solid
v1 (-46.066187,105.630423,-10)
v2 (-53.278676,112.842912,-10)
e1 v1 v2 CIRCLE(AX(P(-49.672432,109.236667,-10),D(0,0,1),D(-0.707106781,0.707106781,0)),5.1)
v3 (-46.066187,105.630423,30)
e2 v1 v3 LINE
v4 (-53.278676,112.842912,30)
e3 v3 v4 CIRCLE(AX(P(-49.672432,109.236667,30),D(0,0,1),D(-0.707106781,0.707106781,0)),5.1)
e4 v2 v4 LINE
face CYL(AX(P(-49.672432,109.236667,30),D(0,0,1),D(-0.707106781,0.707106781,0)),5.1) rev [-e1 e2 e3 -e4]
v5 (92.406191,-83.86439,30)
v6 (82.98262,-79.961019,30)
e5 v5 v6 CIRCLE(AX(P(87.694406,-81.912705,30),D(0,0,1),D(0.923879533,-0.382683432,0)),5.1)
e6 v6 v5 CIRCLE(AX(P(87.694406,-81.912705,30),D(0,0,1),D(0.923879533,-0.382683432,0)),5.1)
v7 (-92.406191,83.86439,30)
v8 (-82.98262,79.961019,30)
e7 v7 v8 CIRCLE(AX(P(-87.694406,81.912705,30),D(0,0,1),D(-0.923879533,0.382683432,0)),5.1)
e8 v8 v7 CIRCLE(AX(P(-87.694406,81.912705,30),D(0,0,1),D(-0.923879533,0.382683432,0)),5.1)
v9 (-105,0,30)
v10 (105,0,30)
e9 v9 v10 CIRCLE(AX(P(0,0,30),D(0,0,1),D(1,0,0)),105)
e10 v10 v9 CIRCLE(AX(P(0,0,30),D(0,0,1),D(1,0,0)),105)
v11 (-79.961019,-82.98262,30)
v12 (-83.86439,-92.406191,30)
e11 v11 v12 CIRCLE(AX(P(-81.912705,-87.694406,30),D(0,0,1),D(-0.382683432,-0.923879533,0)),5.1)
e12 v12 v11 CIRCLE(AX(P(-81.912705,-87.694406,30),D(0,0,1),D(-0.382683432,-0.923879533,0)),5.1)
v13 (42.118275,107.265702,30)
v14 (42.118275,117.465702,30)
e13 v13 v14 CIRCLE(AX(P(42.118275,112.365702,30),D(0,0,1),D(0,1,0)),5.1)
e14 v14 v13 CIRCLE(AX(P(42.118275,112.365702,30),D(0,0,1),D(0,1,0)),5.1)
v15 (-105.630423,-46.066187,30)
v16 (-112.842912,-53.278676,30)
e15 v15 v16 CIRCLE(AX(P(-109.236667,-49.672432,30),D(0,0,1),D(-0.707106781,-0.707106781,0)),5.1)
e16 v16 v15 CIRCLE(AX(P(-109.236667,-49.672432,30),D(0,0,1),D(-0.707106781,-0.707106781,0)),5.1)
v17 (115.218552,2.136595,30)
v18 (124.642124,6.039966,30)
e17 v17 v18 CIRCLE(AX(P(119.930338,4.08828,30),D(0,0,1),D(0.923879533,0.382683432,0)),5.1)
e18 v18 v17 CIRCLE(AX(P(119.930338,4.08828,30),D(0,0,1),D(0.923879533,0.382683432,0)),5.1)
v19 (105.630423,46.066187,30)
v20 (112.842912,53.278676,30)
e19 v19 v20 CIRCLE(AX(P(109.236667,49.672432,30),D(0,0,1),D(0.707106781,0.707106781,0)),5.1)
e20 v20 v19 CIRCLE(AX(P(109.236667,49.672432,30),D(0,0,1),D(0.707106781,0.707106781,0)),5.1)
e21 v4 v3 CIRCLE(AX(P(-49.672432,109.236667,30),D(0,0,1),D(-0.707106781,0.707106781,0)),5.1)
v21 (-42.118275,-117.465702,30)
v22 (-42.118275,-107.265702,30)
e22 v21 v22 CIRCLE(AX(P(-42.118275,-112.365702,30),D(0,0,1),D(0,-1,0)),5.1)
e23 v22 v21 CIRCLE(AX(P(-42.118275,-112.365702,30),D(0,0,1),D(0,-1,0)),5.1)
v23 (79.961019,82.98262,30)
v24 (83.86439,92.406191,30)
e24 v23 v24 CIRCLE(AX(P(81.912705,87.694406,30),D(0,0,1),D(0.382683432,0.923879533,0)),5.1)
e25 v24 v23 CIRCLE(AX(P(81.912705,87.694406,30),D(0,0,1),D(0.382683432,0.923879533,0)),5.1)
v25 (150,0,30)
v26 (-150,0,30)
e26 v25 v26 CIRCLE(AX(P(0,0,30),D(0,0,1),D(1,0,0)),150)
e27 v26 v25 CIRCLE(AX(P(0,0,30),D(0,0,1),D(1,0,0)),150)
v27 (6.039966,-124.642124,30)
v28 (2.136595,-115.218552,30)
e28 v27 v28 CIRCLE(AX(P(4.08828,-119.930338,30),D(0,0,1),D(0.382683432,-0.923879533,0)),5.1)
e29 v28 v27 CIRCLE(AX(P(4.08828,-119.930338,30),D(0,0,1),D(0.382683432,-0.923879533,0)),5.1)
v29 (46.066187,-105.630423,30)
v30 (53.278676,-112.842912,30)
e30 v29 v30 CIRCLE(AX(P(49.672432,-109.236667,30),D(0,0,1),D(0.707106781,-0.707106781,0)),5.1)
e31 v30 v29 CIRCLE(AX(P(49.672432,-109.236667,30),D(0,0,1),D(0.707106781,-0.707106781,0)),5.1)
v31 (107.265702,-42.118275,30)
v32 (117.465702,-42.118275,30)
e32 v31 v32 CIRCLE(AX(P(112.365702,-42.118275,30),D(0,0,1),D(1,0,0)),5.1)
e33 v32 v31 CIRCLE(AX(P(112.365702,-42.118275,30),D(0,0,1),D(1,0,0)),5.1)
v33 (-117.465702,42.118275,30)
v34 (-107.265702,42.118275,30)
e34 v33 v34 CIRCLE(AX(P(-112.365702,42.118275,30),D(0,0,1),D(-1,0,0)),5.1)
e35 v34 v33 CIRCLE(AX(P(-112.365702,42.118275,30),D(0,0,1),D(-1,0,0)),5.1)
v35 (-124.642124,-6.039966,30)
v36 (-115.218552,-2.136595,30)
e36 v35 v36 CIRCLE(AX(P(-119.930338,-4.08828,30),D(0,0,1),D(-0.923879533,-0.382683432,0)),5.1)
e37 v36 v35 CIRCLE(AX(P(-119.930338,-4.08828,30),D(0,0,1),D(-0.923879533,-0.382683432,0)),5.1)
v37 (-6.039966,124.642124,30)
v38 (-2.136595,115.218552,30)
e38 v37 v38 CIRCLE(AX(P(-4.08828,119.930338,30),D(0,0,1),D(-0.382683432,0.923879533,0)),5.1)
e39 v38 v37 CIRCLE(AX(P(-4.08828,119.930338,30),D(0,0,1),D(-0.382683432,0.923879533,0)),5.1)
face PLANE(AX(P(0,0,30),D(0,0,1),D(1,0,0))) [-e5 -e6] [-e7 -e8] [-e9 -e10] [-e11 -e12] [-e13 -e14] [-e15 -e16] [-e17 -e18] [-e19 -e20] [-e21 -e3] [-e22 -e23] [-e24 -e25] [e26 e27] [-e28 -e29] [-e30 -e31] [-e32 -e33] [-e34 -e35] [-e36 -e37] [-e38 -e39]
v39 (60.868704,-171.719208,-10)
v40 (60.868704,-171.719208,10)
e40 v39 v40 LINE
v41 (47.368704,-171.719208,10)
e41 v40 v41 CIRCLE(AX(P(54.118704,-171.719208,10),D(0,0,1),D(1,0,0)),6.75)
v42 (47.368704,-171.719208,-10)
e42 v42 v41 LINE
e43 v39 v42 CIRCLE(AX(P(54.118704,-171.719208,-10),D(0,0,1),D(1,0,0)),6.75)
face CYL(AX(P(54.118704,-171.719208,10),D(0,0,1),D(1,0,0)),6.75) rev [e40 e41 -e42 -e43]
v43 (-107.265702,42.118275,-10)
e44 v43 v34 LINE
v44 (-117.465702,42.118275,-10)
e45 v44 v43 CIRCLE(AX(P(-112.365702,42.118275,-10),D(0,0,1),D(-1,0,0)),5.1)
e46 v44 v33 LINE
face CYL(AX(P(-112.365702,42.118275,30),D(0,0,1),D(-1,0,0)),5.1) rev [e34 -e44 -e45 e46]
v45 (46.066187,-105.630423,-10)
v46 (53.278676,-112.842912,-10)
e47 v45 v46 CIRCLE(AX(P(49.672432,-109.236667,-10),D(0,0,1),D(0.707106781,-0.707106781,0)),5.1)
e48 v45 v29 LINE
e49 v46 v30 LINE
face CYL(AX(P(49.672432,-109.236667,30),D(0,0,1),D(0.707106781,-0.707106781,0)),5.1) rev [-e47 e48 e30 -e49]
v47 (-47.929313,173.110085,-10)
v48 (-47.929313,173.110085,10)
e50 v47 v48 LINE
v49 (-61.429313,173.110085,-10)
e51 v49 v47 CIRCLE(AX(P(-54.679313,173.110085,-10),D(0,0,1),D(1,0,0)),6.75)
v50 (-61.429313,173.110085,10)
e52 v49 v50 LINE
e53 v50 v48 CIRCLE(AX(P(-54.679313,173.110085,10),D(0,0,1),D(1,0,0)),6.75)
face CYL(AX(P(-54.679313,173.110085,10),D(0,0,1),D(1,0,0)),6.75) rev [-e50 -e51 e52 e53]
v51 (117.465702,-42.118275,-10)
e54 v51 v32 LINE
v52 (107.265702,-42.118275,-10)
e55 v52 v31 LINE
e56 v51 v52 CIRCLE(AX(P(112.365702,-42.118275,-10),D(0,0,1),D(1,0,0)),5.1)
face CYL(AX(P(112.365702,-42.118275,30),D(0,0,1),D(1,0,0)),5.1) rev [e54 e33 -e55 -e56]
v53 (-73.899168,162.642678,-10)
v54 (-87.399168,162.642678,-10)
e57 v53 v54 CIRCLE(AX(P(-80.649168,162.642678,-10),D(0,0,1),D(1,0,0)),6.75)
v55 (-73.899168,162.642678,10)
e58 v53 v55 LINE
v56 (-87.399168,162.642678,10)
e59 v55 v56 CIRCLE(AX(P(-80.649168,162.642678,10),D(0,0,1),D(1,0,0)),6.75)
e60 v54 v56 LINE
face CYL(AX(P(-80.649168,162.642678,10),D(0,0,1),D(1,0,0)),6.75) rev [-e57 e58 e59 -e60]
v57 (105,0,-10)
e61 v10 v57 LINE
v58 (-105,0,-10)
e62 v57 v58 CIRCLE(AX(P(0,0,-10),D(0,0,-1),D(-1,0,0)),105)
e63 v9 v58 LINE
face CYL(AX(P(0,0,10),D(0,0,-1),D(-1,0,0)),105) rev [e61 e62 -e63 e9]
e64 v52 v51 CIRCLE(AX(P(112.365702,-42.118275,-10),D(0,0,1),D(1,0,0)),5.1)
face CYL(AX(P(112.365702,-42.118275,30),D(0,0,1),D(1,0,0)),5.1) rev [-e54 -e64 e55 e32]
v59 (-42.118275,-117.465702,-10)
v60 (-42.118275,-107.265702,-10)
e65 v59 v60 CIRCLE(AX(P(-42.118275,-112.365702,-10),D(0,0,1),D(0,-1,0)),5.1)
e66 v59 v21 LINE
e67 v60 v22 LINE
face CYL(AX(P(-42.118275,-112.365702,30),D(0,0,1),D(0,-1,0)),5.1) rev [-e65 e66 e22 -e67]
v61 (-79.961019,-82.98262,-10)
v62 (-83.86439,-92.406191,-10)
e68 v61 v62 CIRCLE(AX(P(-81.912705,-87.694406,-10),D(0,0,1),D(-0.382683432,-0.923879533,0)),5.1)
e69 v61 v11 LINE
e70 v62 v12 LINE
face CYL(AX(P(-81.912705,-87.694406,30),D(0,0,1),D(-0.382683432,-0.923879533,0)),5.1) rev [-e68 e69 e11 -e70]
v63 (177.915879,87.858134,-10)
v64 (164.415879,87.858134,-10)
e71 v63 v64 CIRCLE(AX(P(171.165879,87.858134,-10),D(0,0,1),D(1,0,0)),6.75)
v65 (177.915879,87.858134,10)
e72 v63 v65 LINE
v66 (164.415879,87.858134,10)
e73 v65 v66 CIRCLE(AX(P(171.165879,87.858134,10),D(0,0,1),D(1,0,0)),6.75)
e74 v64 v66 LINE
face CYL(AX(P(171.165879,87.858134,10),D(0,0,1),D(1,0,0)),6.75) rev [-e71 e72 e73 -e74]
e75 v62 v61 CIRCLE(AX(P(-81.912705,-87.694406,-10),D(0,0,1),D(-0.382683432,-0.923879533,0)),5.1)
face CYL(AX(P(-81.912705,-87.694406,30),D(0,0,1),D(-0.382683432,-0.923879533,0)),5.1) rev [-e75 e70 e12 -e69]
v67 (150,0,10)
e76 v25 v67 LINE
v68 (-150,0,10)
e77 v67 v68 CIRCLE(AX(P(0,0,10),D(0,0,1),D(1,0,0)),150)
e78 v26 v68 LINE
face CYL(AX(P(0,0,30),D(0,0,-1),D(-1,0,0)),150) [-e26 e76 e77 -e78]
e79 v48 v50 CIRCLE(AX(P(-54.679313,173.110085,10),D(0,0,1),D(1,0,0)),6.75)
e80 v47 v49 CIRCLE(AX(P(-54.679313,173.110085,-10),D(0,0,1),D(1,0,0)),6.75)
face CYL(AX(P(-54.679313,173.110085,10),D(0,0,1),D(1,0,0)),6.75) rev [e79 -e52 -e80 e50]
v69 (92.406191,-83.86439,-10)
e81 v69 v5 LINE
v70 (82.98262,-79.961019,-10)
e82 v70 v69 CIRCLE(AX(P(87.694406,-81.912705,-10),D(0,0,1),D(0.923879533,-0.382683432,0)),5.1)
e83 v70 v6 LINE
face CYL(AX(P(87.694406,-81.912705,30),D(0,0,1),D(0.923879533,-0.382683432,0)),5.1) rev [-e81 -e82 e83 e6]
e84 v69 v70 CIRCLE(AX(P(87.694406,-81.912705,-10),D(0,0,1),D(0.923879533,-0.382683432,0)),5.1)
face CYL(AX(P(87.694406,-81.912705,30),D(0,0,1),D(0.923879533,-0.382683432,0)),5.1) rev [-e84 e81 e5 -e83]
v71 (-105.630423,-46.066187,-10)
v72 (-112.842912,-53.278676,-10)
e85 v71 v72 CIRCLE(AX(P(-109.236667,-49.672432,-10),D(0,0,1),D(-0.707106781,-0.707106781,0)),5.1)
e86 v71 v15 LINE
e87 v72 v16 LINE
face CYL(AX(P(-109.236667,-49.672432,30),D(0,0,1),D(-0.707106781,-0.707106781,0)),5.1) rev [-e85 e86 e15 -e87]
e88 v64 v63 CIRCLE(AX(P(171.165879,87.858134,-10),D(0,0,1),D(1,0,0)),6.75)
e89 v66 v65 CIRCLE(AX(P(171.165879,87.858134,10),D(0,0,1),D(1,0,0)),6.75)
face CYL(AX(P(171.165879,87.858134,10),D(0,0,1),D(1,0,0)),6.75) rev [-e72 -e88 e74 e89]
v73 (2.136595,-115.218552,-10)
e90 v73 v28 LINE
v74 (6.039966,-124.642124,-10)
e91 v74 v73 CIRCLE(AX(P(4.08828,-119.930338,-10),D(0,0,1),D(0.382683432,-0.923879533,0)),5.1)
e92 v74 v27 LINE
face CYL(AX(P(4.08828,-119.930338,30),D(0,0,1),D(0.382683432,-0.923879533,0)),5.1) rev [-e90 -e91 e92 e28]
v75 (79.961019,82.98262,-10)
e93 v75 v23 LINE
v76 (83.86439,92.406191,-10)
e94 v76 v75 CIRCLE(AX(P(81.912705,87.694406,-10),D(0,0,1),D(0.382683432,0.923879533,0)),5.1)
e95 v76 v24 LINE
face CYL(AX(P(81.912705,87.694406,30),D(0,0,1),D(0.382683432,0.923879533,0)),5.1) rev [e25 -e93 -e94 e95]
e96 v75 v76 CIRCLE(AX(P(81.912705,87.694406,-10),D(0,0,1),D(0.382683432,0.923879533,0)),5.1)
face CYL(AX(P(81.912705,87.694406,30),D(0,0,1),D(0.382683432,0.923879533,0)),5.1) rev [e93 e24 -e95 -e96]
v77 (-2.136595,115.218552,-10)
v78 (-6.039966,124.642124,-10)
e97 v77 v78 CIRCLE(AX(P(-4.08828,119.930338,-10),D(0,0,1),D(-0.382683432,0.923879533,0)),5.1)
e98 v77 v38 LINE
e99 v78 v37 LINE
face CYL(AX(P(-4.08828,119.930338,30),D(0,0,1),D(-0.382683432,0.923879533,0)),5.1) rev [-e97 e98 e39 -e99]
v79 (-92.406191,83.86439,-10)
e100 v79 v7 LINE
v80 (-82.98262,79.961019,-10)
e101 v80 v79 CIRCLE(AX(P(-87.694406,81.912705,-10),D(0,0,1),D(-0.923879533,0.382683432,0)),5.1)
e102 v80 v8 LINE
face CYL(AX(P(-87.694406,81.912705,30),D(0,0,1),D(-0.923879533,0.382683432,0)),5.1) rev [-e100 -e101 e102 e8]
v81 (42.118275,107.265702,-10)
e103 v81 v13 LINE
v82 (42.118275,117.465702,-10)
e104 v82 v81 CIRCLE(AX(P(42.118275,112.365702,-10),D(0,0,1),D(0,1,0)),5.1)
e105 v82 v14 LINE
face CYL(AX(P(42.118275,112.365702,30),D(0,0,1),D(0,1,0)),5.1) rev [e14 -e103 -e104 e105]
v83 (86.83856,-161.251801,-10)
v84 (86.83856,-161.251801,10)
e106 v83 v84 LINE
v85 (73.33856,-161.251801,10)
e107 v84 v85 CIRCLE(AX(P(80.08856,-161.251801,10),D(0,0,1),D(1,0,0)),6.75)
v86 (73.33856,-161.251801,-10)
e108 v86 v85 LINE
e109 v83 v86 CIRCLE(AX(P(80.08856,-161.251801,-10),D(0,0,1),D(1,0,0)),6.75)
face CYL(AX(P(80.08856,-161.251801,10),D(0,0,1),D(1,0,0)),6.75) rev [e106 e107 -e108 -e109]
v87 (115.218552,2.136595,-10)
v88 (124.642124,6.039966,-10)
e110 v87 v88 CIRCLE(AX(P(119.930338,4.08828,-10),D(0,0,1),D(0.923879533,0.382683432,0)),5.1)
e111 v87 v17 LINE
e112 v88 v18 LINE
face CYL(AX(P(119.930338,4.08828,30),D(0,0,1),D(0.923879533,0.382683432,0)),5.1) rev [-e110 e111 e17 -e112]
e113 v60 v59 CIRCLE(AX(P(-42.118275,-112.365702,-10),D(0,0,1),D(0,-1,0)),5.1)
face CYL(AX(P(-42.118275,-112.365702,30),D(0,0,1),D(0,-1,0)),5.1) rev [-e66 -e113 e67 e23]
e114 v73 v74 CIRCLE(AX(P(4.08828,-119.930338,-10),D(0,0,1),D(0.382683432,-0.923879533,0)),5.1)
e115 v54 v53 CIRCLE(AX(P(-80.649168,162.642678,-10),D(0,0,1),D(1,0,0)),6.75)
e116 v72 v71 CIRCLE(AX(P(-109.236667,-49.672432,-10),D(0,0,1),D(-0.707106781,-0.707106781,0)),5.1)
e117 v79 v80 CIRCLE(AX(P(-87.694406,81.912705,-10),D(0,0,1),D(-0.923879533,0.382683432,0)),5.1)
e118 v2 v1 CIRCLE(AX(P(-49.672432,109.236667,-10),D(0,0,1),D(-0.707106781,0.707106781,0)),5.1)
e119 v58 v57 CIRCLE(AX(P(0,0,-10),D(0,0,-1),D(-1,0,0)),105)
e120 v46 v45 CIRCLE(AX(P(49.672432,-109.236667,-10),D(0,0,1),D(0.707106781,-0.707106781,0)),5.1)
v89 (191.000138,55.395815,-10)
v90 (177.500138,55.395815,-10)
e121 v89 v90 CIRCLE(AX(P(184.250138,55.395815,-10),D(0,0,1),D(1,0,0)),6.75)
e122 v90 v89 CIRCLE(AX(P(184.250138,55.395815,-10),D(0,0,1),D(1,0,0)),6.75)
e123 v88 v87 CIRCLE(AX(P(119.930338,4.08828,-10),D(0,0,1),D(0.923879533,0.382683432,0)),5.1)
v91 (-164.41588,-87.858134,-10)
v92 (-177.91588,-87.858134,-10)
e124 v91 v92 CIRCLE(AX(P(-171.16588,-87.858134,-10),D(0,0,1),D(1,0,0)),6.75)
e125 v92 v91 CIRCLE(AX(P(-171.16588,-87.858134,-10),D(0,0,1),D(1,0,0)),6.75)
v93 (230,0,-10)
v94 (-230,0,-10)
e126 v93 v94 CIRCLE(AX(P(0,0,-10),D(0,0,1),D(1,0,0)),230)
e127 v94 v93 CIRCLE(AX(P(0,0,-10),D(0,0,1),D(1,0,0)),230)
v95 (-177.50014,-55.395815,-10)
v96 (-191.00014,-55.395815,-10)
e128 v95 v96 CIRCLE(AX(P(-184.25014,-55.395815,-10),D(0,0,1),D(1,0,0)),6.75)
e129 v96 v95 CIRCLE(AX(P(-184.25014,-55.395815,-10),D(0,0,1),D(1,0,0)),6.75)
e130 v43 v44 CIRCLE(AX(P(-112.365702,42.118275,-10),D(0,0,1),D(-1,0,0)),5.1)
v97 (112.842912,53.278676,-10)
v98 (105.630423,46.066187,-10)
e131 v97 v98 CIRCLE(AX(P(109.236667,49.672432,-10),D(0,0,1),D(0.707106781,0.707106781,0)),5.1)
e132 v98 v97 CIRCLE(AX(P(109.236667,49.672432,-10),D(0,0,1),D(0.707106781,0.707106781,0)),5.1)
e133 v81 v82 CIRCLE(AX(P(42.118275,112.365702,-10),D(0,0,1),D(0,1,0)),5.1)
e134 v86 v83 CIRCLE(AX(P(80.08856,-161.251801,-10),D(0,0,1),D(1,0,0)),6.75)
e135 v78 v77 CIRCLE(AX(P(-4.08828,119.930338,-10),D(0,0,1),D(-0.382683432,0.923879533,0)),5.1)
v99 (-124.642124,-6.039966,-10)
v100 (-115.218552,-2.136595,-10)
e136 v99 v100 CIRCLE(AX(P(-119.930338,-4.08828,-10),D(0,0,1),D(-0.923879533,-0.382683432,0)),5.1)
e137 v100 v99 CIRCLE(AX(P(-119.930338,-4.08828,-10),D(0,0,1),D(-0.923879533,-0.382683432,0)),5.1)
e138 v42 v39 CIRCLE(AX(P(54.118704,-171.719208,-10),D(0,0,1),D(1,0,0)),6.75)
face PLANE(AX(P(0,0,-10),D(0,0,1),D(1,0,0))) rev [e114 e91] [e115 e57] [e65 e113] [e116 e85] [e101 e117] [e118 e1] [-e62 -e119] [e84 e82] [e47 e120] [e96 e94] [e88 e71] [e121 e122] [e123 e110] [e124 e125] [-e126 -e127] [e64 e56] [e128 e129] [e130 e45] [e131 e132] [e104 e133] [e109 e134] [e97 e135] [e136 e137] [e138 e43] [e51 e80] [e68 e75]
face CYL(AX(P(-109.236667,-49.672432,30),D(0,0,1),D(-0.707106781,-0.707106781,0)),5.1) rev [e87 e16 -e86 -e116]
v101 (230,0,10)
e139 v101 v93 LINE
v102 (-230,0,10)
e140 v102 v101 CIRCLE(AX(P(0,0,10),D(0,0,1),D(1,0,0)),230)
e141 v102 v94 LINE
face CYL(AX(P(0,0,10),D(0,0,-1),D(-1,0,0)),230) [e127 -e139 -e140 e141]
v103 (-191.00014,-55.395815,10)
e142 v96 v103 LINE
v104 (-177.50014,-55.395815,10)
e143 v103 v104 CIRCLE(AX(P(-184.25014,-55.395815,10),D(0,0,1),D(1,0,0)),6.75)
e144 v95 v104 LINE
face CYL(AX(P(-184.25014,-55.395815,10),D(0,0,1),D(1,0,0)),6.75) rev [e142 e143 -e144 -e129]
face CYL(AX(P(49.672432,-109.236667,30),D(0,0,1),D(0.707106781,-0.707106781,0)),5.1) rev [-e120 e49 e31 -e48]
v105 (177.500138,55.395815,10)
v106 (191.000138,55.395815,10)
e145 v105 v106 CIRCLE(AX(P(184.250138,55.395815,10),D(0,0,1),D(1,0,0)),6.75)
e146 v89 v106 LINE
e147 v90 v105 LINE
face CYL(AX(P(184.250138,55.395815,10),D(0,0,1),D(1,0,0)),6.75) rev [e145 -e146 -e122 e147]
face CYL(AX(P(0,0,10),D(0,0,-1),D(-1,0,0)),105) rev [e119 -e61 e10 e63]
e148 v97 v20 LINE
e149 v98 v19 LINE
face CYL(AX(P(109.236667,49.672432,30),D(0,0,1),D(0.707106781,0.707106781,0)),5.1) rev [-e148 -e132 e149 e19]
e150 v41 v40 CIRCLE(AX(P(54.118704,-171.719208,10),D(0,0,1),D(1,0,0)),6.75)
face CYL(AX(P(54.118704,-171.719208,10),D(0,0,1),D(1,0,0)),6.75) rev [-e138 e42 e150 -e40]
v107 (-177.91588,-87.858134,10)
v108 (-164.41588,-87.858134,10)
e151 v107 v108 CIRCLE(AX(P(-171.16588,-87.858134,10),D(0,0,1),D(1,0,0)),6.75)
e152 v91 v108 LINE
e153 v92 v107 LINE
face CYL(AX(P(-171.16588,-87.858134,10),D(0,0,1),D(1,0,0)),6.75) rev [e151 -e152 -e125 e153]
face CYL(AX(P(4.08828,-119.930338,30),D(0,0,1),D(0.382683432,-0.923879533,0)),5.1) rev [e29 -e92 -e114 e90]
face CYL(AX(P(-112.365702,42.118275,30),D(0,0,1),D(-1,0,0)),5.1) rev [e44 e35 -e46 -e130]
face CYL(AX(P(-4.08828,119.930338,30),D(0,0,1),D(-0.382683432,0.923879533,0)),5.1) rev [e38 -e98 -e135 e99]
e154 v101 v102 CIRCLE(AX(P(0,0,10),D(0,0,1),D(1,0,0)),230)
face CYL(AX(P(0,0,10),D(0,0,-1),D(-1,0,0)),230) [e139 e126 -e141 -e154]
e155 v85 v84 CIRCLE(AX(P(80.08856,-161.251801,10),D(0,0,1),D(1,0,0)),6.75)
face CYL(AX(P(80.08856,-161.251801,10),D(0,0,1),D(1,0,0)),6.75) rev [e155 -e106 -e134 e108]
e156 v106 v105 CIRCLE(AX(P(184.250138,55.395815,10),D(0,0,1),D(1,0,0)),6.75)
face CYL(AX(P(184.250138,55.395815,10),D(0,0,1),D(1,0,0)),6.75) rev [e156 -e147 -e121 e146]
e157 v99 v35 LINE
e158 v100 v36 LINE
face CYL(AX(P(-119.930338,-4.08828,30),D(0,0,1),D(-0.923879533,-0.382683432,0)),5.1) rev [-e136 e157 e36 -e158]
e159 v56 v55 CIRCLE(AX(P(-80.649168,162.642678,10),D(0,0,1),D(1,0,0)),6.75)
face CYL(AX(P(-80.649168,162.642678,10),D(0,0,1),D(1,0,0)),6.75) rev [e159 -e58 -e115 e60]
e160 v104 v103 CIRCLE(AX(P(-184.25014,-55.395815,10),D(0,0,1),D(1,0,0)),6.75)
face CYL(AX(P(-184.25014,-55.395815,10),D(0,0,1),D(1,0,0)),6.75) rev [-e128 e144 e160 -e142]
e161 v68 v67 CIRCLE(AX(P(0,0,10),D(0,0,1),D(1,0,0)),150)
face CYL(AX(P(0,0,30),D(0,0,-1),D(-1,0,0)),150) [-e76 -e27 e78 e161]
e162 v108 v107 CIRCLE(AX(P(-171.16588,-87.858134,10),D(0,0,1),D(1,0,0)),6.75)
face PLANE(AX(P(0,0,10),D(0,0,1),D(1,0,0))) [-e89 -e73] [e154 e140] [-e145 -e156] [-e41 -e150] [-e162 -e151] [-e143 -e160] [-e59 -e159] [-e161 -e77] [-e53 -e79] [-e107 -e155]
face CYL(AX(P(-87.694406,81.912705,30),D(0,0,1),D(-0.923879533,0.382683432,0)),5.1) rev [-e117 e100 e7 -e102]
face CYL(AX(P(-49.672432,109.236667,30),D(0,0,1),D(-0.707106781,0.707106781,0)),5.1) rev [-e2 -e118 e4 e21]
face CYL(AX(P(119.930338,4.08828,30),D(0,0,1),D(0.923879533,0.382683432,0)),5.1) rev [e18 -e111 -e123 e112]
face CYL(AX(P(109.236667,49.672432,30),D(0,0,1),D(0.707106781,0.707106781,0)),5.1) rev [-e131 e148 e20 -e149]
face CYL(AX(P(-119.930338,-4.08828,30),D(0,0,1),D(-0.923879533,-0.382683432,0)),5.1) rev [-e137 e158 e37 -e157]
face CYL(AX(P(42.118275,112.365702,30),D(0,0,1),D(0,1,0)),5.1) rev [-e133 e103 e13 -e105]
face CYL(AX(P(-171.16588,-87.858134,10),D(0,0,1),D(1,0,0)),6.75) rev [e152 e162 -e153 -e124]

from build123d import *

# Parameters (mm, degrees)
SKETCH_1_R               = 230
EXTRUDE_1_DEPTH          = 10
SKETCH_2_R               = 105
CUT_EXTRUDE_1_DEPTH      = 326.883414736
SKETCH_3_R               = 150
SKETCH_3_R_2             = 105
EXTRUDE_2_DEPTH          = 20
HOLE_WIZARD_M12_1_D      = 10.2
PATTERN_CIRCULAR_1_COUNT = 16
HOLE_WIZARD_M12_1_2_D    = 13.5


with BuildPart() as part:
    # 草图1 → 凸台-拉伸1 (new, symmetric)
    with BuildSketch(Plane.XY):
        Circle(SKETCH_1_R)
    extrude(amount=EXTRUDE_1_DEPTH, both=True)

    # 草图2 → 切除-拉伸1 (cut, through all)
    with BuildSketch(Plane(origin=(0, 0, -10), x_dir=(-1, 0, 0), z_dir=(0, 0, -1))):
        Circle(SKETCH_2_R)
    extrude(amount=-CUT_EXTRUDE_1_DEPTH, mode=Mode.SUBTRACT)

    # 草图3 → 凸台-拉伸2 (add)
    with BuildSketch(Plane.XY.offset(10)):
        Circle(SKETCH_3_R)
        with Locations(Location((0, 0, 0), (0, 0, 180))):
            Circle(SKETCH_3_R_2, mode=Mode.SUBTRACT)
    extrude(amount=EXTRUDE_2_DEPTH)

    # Hole Wizard M12 _1 (through all)
    with Locations(Plane.XY.offset(30)):
        with Locations((112.365701655, -42.118275031)):
            hole_wizard_m12_1 = Hole(HOLE_WIZARD_M12_1_D / 2)

    # 阵列(圆周)1: Hole Wizard M12 _1 ×16 about axis
    pattern_circular_1_axis = Axis((0, 0, 0), (0, 0, 1))
    for i in range(1, PATTERN_CIRCULAR_1_COUNT):
        add(hole_wizard_m12_1.rotate(pattern_circular_1_axis, i * 360 / PATTERN_CIRCULAR_1_COUNT), mode=Mode.SUBTRACT)

    # Hole Wizard M12 _1 2 (through all)
    with Locations(Plane.XY.offset(10)):
        with Locations((54.118704372, -171.719208219), (80.088559574, -161.251800671), (171.165878787, 87.858133743), (184.250138222, 55.395814741), (-171.165880115, -87.858134279), (-184.25013955, -55.395815276), (-80.649167813, 162.642677508), (-54.679312611, 173.110085056)):
            Hole(HOLE_WIZARD_M12_1_2_D / 2)


solid = part.part
